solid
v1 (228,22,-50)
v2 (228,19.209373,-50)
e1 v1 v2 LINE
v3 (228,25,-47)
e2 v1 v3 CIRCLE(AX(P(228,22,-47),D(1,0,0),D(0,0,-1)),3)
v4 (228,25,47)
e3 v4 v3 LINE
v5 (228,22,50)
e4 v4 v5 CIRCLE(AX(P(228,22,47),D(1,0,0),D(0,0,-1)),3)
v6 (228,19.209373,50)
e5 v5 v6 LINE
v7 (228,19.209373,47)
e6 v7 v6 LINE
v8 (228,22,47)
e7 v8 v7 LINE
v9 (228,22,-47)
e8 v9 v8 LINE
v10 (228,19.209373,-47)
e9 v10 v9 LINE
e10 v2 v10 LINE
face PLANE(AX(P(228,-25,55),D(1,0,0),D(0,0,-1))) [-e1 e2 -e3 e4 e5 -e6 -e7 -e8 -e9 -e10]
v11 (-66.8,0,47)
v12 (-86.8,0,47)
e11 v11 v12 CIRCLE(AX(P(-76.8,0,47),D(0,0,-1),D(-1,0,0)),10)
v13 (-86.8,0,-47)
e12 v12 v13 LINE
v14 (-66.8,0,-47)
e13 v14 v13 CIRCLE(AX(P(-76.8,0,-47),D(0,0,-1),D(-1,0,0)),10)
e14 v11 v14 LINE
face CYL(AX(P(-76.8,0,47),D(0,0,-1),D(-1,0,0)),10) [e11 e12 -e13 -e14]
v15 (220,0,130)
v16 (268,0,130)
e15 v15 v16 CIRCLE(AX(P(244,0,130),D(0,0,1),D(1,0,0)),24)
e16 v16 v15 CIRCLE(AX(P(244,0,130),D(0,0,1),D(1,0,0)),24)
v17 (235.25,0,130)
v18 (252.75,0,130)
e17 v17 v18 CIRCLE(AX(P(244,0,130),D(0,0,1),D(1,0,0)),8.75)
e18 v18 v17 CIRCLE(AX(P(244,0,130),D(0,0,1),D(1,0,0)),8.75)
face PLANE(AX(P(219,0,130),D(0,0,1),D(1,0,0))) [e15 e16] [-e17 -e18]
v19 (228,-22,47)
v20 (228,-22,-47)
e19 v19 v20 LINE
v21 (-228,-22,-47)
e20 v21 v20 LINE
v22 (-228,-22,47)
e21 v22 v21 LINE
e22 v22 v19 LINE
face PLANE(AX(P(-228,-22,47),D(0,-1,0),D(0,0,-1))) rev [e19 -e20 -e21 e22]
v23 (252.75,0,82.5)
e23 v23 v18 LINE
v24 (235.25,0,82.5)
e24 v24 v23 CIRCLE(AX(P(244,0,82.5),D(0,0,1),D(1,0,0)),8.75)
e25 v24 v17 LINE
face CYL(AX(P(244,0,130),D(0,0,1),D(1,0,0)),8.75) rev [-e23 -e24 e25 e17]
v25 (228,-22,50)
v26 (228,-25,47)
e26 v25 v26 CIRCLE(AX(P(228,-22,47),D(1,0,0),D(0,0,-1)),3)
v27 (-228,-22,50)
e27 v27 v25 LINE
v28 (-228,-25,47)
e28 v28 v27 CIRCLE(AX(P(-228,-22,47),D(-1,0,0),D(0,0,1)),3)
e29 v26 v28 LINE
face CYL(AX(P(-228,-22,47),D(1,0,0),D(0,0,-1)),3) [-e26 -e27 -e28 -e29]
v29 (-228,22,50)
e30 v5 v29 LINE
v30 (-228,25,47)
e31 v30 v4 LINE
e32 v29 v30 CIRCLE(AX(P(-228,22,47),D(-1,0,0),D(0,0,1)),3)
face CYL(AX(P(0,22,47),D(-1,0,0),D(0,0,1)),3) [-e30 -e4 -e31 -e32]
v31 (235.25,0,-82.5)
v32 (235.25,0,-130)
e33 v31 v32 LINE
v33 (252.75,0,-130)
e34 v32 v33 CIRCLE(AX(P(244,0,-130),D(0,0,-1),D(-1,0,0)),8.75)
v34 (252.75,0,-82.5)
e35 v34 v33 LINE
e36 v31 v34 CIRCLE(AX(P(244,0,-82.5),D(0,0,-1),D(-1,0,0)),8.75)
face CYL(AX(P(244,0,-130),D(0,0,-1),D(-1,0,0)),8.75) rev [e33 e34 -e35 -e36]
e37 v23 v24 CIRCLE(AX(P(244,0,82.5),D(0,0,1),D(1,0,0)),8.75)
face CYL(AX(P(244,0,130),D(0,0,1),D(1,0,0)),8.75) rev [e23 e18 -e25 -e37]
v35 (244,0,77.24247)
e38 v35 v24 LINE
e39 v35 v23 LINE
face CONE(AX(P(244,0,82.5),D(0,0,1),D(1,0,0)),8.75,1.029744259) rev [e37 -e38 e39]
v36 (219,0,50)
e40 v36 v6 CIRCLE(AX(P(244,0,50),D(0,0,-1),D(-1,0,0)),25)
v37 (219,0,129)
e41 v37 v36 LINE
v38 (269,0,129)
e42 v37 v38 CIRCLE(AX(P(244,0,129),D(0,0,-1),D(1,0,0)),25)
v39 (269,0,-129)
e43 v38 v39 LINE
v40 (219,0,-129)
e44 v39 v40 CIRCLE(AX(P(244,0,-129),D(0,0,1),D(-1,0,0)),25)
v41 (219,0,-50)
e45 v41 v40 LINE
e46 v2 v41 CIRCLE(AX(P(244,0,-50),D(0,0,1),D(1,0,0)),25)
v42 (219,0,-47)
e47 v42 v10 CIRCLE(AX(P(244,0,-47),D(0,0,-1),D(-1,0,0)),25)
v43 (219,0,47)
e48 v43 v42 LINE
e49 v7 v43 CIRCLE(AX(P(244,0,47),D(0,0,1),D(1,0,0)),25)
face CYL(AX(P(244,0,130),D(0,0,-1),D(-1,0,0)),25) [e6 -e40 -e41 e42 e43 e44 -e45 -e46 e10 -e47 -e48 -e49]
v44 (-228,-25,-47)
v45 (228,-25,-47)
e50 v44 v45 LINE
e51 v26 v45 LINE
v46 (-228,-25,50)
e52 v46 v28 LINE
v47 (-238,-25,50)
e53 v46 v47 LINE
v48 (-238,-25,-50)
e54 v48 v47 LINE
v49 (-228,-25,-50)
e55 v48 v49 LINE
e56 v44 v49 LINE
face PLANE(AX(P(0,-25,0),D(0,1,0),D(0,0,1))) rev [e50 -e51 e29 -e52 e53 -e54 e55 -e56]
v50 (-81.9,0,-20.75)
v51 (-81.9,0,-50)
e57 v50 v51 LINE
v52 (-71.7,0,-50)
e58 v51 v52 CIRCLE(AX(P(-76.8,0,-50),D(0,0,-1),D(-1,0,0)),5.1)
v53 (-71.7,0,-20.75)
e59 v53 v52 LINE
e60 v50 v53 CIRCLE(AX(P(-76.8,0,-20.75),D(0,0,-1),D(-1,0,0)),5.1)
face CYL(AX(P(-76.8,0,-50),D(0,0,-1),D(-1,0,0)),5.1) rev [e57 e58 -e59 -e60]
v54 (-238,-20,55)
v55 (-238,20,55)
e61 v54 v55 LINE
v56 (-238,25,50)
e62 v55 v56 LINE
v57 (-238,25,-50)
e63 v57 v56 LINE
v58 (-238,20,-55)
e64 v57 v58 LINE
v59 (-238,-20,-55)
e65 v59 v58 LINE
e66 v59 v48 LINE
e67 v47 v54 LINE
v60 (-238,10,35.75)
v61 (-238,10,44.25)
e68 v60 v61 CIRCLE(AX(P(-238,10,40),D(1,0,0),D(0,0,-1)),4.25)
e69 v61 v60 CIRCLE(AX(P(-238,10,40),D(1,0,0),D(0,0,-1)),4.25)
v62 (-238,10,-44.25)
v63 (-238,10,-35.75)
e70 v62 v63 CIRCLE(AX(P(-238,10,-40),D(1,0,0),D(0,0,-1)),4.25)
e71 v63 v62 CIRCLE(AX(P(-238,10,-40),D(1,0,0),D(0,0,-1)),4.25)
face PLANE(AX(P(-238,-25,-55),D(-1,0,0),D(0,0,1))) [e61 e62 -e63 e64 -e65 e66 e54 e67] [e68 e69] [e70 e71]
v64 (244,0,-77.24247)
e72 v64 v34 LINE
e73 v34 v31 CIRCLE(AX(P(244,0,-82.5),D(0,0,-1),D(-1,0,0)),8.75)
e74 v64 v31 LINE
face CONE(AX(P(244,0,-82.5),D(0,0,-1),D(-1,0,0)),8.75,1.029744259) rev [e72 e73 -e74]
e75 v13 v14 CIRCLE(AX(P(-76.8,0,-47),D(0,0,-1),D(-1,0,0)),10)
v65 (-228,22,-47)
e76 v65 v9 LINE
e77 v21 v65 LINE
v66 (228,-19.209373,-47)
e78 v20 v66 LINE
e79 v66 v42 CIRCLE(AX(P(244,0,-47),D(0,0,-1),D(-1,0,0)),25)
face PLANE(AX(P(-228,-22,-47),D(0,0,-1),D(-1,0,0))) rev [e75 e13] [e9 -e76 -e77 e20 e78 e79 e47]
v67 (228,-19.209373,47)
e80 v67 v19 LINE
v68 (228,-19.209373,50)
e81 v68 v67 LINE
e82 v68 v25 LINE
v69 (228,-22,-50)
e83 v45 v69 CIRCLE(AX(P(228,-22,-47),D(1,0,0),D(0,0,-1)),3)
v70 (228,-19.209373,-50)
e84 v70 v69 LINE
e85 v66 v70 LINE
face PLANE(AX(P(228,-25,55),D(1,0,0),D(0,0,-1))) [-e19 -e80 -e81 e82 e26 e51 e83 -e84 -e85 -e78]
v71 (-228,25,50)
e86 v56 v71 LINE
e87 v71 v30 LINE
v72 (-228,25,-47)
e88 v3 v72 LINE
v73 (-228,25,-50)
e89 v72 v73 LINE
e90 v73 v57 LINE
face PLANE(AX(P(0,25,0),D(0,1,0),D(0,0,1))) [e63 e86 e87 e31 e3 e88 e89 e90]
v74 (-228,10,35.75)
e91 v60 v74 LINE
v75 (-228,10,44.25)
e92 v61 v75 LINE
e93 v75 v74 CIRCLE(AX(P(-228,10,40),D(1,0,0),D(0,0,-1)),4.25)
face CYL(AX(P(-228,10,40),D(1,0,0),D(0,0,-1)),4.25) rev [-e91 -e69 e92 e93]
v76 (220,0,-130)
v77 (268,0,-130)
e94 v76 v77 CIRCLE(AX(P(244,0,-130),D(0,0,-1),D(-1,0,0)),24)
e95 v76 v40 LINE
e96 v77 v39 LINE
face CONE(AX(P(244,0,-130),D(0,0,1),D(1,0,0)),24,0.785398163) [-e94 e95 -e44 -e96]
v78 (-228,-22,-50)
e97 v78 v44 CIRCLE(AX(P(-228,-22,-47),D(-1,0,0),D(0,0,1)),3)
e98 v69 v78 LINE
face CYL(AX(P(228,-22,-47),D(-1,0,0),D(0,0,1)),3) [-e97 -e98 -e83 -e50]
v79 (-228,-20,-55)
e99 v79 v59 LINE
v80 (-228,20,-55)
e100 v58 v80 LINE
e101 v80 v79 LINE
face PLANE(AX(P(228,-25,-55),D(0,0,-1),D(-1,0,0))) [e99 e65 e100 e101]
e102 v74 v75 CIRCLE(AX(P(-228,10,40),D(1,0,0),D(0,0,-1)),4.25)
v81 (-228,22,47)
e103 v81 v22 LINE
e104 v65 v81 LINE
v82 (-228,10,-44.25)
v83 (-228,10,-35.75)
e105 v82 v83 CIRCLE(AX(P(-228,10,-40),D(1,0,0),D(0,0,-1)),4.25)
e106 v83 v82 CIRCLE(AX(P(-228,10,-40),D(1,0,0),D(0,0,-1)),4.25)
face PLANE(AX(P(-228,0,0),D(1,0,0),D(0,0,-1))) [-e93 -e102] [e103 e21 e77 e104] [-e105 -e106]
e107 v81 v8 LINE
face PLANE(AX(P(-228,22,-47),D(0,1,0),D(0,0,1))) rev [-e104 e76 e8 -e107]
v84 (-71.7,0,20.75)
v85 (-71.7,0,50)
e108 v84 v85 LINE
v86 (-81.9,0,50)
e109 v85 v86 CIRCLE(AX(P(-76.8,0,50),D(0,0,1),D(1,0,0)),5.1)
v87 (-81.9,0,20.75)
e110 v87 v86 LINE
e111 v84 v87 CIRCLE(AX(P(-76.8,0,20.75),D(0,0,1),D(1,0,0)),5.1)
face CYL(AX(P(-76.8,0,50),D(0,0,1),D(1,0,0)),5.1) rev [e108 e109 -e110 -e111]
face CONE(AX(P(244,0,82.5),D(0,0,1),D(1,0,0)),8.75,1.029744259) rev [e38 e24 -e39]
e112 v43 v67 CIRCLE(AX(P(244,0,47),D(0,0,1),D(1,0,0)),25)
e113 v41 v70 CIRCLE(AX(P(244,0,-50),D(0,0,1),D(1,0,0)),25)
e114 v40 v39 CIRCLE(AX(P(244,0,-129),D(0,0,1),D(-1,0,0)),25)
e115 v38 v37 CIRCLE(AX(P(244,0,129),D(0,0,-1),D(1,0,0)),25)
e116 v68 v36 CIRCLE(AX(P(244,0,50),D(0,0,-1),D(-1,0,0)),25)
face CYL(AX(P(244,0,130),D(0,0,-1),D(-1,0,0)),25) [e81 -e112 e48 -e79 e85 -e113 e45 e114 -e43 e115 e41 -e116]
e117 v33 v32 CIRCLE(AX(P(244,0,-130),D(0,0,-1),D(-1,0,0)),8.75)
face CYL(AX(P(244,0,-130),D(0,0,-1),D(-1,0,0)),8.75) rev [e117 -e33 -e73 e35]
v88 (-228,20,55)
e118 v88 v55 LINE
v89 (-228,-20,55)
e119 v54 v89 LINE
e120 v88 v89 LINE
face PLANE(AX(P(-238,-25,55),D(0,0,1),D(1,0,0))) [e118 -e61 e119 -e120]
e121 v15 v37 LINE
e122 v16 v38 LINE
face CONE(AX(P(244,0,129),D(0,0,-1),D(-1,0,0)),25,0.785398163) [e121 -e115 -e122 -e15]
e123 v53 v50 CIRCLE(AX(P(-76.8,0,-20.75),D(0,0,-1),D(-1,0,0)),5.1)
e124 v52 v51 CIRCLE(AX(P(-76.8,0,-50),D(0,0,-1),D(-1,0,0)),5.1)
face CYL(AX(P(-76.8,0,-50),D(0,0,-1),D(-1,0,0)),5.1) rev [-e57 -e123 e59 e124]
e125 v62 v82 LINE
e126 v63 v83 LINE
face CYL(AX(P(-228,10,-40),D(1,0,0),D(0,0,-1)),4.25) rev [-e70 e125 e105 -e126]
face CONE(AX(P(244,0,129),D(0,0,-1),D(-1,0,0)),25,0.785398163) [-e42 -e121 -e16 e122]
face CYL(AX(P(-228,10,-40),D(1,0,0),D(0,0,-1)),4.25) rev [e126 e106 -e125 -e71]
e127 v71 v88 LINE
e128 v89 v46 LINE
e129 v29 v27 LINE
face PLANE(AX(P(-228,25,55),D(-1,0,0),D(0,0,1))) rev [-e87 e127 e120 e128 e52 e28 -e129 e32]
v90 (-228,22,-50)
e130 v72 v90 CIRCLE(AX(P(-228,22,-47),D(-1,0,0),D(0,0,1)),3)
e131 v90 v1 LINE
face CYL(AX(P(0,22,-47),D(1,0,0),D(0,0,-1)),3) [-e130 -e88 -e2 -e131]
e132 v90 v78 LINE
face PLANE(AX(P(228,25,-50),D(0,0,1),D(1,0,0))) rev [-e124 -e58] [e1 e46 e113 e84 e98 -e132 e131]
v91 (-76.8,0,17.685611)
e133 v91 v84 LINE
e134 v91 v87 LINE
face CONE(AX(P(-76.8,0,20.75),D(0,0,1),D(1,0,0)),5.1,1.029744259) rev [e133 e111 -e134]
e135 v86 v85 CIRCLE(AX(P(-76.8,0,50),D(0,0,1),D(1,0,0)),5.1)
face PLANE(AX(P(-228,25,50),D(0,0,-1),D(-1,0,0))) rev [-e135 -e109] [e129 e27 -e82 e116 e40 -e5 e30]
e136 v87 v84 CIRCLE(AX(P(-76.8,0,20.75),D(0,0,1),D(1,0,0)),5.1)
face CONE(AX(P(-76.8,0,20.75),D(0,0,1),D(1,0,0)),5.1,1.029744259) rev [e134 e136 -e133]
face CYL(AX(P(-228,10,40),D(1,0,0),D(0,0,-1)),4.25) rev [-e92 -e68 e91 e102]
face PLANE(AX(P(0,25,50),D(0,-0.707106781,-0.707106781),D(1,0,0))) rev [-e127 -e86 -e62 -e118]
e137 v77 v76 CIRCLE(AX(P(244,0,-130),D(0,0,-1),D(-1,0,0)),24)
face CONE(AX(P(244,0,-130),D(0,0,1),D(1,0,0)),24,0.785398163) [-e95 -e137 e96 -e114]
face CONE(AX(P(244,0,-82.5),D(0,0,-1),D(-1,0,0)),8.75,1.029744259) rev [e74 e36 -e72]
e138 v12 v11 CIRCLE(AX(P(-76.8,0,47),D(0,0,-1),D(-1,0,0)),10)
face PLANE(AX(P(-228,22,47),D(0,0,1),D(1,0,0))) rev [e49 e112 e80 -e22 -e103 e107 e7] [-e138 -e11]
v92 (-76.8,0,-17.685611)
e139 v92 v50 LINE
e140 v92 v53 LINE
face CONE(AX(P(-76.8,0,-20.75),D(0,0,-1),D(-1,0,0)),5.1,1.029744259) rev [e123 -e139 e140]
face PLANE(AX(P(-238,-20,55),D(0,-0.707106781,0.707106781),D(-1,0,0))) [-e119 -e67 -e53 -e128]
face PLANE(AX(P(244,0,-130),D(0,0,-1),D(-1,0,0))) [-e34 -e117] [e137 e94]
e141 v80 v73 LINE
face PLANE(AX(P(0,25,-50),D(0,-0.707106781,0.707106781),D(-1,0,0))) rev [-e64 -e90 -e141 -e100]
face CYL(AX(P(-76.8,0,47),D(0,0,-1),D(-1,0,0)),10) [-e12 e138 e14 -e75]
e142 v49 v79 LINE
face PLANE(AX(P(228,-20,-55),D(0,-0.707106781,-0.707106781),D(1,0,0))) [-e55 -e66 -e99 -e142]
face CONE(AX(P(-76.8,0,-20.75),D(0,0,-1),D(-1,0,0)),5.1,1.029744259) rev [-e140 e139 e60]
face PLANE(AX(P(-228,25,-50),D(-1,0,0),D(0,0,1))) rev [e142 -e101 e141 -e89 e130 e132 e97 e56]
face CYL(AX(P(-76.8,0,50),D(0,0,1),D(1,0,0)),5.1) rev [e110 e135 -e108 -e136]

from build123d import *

# Parameters (mm, degrees)
SKETCH_1_W                    = 466
SKETCH_1_H                    = 110
EXTRUDE_1_DEPTH               = 50
SKETCH_2_W                    = 456
SKETCH_2_H                    = 5
CUT_EXTRUDE_1_DEPTH           = 250.337121183
SKETCH_3_W                    = 456
SKETCH_3_H                    = 5
CUT_EXTRUDE_2_DEPTH           = 250.337121183
SKETCH_4_W                    = 94
SKETCH_4_H                    = 44
CUT_EXTRUDE_3_DEPTH           = 456
SKETCH_5_W                    = 10
SKETCH_5_H                    = 94
SKETCH_6_W                    = 25
SKETCH_6_H                    = 260
HOLE_WIZARD_8_5_8_5_1_D       = 8.5
HOLE_WIZARD_8_5_8_5_1_DEPTH   = 10
HOLE_WIZARD_M12_3_D           = 10.2
HOLE_WIZARD_M12_3_DEPTH       = 29.25
HOLE_WIZARD_M12_3_TIP         = 3.064389157
HOLE_WIZARD_M12_4_D           = 10.2
HOLE_WIZARD_M12_4_DEPTH       = 29.25
HOLE_WIZARD_M12_4_TIP         = 3.064389157
HOLE_WIZARD_10_2_10_2_2_D     = 10.2
HOLE_WIZARD_10_2_10_2_2_DEPTH = 29.25
HOLE_WIZARD_10_2_10_2_2_TIP   = 3.064389157
CHAMFER_1_SIZE                = 1
FILLET_1_R                    = 3
CHAMFER_2_SIZE                = 5
HOLE_WIZARD_M20_1_D           = 17.5
HOLE_WIZARD_M20_1_DEPTH       = 47.5
HOLE_WIZARD_M20_1_TIP         = 5.257530416
HOLE_WIZARD_M20_2_D           = 17.5
HOLE_WIZARD_M20_2_DEPTH       = 47.5
HOLE_WIZARD_M20_2_TIP         = 5.257530416


with BuildPart() as part:
    # 草图1 → 凸台-拉伸1 (new body)
    with BuildSketch(Plane(origin=(0, 25, 0), x_dir=(1, 0, 0), z_dir=(0, 1, 0))):
        with Locations((-5, 0)):
            Rectangle(SKETCH_1_W, SKETCH_1_H)
    extrude(amount=-EXTRUDE_1_DEPTH)

    # 草图2 → 切除-拉伸1 (cut, through all)
    with BuildSketch(Plane.XZ.offset(25)):
        with Locations((0, -52.5)):
            Rectangle(SKETCH_2_W, SKETCH_2_H)
    extrude(amount=-CUT_EXTRUDE_1_DEPTH, mode=Mode.SUBTRACT)

    # 草图3 → 切除-拉伸2 (cut, through all)
    with BuildSketch(Plane.XZ.offset(25)):
        with Locations((0, 52.5)):
            Rectangle(SKETCH_3_W, SKETCH_3_H)
    extrude(amount=-CUT_EXTRUDE_2_DEPTH, mode=Mode.SUBTRACT)

    # 草图4 → 切除-拉伸3 (cut)
    with BuildSketch(Plane(origin=(228, 0, 0), x_dir=(0, 0, -1), z_dir=(1, 0, 0))):
        Rectangle(SKETCH_4_W, SKETCH_4_H)
    extrude(amount=-CUT_EXTRUDE_3_DEPTH, mode=Mode.SUBTRACT)

    # 草图5 → 旋转1 (revolve)
    with BuildSketch(Plane.XZ, mode=Mode.PRIVATE) as revolve_1_sk:
        with Locations((-71.8, 0)):
            Rectangle(SKETCH_5_W, SKETCH_5_H)
    revolve(revolve_1_sk.sketch.rotate(Axis((-76.8, 0, 47), (0, 0, -1)), 180), axis=Axis((-76.8, 0, 47), (0, 0, -1)))

    # 草图6 → 旋转2 (revolve)
    with BuildSketch(Plane(origin=(0, 0, 0), x_dir=(1, 0, 0), z_dir=(0, 1, 0))):
        with Locations((231.5, 0)):
            Rectangle(SKETCH_6_W, SKETCH_6_H)
    revolve(axis=Axis((244, 0, 130), (0, 0, -1)))

    # Ø8.5 (8.5) 直径孔1
    with Locations(Plane(origin=(-228, 0, 0), x_dir=(0, 0, -1), z_dir=(1, 0, 0))):
        with Locations((40, 10), (-40, 10)):
            Hole(HOLE_WIZARD_8_5_8_5_1_D / 2, depth=HOLE_WIZARD_8_5_8_5_1_DEPTH)

    # M12 螺纹孔3
    with Locations(Plane.XY.offset(50)):
        with Locations((-76.8, 0)):
            Hole(HOLE_WIZARD_M12_3_D / 2, depth=HOLE_WIZARD_M12_3_DEPTH)
            with Locations((0, 0, -(HOLE_WIZARD_M12_3_DEPTH + HOLE_WIZARD_M12_3_TIP / 2))):  # 118° drill point
                Cone(0, HOLE_WIZARD_M12_3_D / 2, HOLE_WIZARD_M12_3_TIP, mode=Mode.SUBTRACT)

    # M12 螺纹孔4
    with Locations(Plane(origin=(0, 0, -50), x_dir=(-1, 0, 0), z_dir=(0, 0, -1))):
        with Locations((76.8, 0)):
            Hole(HOLE_WIZARD_M12_4_D / 2, depth=HOLE_WIZARD_M12_4_DEPTH)
            with Locations((0, 0, -(HOLE_WIZARD_M12_4_DEPTH + HOLE_WIZARD_M12_4_TIP / 2))):  # 118° drill point
                Cone(0, HOLE_WIZARD_M12_4_D / 2, HOLE_WIZARD_M12_4_TIP, mode=Mode.SUBTRACT)

    # Ø10.2 (10.2) 直径孔2
    with Locations(Plane(origin=(0, 0, -50), x_dir=(-1, 0, 0), z_dir=(0, 0, -1))):
        with Locations((76.8, 0)):
            Hole(HOLE_WIZARD_10_2_10_2_2_D / 2, depth=HOLE_WIZARD_10_2_10_2_2_DEPTH)
            with Locations((0, 0, -(HOLE_WIZARD_10_2_10_2_2_DEPTH + HOLE_WIZARD_10_2_10_2_2_TIP / 2))):  # 118° drill point
                Cone(0, HOLE_WIZARD_10_2_10_2_2_D / 2, HOLE_WIZARD_10_2_10_2_2_TIP, mode=Mode.SUBTRACT)

    # 倒角1
    chamfer_1_edges = [part.edges().sort_by_distance(p)[0] for p in [
        (269, 0, 130),
        (269, 0, -130),
    ]]
    chamfer(chamfer_1_edges, length=CHAMFER_1_SIZE)

    # 圆角1
    fillet_1_edges = [part.edges().sort_by_distance(p)[0] for p in [
        (0, 25, -50),
        (0, -25, -50),
        (0, 25, 50),
        (0, -25, 50),
    ]]
    fillet(fillet_1_edges, radius=FILLET_1_R)

    # 倒角2
    chamfer_2_edges = [part.edges().sort_by_distance(p)[0] for p in [
        (-233, 25, -55),
        (-233, -25, -55),
        (-233, -25, 55),
        (-233, 25, 55),
    ]]
    chamfer(chamfer_2_edges, length=CHAMFER_2_SIZE)

    # M20 螺纹孔1
    with Locations(Plane.XY.offset(130)):
        with Locations((244, 0)):
            Hole(HOLE_WIZARD_M20_1_D / 2, depth=HOLE_WIZARD_M20_1_DEPTH)
            with Locations((0, 0, -(HOLE_WIZARD_M20_1_DEPTH + HOLE_WIZARD_M20_1_TIP / 2))):  # 118° drill point
                Cone(0, HOLE_WIZARD_M20_1_D / 2, HOLE_WIZARD_M20_1_TIP, mode=Mode.SUBTRACT)

    # M20 螺纹孔2
    with Locations(Plane(origin=(0, 0, -130), x_dir=(-1, 0, 0), z_dir=(0, 0, -1))):
        with Locations((-244, 0)):
            Hole(HOLE_WIZARD_M20_2_D / 2, depth=HOLE_WIZARD_M20_2_DEPTH)
            with Locations((0, 0, -(HOLE_WIZARD_M20_2_DEPTH + HOLE_WIZARD_M20_2_TIP / 2))):  # 118° drill point
                Cone(0, HOLE_WIZARD_M20_2_D / 2, HOLE_WIZARD_M20_2_TIP, mode=Mode.SUBTRACT)


solid = part.part
